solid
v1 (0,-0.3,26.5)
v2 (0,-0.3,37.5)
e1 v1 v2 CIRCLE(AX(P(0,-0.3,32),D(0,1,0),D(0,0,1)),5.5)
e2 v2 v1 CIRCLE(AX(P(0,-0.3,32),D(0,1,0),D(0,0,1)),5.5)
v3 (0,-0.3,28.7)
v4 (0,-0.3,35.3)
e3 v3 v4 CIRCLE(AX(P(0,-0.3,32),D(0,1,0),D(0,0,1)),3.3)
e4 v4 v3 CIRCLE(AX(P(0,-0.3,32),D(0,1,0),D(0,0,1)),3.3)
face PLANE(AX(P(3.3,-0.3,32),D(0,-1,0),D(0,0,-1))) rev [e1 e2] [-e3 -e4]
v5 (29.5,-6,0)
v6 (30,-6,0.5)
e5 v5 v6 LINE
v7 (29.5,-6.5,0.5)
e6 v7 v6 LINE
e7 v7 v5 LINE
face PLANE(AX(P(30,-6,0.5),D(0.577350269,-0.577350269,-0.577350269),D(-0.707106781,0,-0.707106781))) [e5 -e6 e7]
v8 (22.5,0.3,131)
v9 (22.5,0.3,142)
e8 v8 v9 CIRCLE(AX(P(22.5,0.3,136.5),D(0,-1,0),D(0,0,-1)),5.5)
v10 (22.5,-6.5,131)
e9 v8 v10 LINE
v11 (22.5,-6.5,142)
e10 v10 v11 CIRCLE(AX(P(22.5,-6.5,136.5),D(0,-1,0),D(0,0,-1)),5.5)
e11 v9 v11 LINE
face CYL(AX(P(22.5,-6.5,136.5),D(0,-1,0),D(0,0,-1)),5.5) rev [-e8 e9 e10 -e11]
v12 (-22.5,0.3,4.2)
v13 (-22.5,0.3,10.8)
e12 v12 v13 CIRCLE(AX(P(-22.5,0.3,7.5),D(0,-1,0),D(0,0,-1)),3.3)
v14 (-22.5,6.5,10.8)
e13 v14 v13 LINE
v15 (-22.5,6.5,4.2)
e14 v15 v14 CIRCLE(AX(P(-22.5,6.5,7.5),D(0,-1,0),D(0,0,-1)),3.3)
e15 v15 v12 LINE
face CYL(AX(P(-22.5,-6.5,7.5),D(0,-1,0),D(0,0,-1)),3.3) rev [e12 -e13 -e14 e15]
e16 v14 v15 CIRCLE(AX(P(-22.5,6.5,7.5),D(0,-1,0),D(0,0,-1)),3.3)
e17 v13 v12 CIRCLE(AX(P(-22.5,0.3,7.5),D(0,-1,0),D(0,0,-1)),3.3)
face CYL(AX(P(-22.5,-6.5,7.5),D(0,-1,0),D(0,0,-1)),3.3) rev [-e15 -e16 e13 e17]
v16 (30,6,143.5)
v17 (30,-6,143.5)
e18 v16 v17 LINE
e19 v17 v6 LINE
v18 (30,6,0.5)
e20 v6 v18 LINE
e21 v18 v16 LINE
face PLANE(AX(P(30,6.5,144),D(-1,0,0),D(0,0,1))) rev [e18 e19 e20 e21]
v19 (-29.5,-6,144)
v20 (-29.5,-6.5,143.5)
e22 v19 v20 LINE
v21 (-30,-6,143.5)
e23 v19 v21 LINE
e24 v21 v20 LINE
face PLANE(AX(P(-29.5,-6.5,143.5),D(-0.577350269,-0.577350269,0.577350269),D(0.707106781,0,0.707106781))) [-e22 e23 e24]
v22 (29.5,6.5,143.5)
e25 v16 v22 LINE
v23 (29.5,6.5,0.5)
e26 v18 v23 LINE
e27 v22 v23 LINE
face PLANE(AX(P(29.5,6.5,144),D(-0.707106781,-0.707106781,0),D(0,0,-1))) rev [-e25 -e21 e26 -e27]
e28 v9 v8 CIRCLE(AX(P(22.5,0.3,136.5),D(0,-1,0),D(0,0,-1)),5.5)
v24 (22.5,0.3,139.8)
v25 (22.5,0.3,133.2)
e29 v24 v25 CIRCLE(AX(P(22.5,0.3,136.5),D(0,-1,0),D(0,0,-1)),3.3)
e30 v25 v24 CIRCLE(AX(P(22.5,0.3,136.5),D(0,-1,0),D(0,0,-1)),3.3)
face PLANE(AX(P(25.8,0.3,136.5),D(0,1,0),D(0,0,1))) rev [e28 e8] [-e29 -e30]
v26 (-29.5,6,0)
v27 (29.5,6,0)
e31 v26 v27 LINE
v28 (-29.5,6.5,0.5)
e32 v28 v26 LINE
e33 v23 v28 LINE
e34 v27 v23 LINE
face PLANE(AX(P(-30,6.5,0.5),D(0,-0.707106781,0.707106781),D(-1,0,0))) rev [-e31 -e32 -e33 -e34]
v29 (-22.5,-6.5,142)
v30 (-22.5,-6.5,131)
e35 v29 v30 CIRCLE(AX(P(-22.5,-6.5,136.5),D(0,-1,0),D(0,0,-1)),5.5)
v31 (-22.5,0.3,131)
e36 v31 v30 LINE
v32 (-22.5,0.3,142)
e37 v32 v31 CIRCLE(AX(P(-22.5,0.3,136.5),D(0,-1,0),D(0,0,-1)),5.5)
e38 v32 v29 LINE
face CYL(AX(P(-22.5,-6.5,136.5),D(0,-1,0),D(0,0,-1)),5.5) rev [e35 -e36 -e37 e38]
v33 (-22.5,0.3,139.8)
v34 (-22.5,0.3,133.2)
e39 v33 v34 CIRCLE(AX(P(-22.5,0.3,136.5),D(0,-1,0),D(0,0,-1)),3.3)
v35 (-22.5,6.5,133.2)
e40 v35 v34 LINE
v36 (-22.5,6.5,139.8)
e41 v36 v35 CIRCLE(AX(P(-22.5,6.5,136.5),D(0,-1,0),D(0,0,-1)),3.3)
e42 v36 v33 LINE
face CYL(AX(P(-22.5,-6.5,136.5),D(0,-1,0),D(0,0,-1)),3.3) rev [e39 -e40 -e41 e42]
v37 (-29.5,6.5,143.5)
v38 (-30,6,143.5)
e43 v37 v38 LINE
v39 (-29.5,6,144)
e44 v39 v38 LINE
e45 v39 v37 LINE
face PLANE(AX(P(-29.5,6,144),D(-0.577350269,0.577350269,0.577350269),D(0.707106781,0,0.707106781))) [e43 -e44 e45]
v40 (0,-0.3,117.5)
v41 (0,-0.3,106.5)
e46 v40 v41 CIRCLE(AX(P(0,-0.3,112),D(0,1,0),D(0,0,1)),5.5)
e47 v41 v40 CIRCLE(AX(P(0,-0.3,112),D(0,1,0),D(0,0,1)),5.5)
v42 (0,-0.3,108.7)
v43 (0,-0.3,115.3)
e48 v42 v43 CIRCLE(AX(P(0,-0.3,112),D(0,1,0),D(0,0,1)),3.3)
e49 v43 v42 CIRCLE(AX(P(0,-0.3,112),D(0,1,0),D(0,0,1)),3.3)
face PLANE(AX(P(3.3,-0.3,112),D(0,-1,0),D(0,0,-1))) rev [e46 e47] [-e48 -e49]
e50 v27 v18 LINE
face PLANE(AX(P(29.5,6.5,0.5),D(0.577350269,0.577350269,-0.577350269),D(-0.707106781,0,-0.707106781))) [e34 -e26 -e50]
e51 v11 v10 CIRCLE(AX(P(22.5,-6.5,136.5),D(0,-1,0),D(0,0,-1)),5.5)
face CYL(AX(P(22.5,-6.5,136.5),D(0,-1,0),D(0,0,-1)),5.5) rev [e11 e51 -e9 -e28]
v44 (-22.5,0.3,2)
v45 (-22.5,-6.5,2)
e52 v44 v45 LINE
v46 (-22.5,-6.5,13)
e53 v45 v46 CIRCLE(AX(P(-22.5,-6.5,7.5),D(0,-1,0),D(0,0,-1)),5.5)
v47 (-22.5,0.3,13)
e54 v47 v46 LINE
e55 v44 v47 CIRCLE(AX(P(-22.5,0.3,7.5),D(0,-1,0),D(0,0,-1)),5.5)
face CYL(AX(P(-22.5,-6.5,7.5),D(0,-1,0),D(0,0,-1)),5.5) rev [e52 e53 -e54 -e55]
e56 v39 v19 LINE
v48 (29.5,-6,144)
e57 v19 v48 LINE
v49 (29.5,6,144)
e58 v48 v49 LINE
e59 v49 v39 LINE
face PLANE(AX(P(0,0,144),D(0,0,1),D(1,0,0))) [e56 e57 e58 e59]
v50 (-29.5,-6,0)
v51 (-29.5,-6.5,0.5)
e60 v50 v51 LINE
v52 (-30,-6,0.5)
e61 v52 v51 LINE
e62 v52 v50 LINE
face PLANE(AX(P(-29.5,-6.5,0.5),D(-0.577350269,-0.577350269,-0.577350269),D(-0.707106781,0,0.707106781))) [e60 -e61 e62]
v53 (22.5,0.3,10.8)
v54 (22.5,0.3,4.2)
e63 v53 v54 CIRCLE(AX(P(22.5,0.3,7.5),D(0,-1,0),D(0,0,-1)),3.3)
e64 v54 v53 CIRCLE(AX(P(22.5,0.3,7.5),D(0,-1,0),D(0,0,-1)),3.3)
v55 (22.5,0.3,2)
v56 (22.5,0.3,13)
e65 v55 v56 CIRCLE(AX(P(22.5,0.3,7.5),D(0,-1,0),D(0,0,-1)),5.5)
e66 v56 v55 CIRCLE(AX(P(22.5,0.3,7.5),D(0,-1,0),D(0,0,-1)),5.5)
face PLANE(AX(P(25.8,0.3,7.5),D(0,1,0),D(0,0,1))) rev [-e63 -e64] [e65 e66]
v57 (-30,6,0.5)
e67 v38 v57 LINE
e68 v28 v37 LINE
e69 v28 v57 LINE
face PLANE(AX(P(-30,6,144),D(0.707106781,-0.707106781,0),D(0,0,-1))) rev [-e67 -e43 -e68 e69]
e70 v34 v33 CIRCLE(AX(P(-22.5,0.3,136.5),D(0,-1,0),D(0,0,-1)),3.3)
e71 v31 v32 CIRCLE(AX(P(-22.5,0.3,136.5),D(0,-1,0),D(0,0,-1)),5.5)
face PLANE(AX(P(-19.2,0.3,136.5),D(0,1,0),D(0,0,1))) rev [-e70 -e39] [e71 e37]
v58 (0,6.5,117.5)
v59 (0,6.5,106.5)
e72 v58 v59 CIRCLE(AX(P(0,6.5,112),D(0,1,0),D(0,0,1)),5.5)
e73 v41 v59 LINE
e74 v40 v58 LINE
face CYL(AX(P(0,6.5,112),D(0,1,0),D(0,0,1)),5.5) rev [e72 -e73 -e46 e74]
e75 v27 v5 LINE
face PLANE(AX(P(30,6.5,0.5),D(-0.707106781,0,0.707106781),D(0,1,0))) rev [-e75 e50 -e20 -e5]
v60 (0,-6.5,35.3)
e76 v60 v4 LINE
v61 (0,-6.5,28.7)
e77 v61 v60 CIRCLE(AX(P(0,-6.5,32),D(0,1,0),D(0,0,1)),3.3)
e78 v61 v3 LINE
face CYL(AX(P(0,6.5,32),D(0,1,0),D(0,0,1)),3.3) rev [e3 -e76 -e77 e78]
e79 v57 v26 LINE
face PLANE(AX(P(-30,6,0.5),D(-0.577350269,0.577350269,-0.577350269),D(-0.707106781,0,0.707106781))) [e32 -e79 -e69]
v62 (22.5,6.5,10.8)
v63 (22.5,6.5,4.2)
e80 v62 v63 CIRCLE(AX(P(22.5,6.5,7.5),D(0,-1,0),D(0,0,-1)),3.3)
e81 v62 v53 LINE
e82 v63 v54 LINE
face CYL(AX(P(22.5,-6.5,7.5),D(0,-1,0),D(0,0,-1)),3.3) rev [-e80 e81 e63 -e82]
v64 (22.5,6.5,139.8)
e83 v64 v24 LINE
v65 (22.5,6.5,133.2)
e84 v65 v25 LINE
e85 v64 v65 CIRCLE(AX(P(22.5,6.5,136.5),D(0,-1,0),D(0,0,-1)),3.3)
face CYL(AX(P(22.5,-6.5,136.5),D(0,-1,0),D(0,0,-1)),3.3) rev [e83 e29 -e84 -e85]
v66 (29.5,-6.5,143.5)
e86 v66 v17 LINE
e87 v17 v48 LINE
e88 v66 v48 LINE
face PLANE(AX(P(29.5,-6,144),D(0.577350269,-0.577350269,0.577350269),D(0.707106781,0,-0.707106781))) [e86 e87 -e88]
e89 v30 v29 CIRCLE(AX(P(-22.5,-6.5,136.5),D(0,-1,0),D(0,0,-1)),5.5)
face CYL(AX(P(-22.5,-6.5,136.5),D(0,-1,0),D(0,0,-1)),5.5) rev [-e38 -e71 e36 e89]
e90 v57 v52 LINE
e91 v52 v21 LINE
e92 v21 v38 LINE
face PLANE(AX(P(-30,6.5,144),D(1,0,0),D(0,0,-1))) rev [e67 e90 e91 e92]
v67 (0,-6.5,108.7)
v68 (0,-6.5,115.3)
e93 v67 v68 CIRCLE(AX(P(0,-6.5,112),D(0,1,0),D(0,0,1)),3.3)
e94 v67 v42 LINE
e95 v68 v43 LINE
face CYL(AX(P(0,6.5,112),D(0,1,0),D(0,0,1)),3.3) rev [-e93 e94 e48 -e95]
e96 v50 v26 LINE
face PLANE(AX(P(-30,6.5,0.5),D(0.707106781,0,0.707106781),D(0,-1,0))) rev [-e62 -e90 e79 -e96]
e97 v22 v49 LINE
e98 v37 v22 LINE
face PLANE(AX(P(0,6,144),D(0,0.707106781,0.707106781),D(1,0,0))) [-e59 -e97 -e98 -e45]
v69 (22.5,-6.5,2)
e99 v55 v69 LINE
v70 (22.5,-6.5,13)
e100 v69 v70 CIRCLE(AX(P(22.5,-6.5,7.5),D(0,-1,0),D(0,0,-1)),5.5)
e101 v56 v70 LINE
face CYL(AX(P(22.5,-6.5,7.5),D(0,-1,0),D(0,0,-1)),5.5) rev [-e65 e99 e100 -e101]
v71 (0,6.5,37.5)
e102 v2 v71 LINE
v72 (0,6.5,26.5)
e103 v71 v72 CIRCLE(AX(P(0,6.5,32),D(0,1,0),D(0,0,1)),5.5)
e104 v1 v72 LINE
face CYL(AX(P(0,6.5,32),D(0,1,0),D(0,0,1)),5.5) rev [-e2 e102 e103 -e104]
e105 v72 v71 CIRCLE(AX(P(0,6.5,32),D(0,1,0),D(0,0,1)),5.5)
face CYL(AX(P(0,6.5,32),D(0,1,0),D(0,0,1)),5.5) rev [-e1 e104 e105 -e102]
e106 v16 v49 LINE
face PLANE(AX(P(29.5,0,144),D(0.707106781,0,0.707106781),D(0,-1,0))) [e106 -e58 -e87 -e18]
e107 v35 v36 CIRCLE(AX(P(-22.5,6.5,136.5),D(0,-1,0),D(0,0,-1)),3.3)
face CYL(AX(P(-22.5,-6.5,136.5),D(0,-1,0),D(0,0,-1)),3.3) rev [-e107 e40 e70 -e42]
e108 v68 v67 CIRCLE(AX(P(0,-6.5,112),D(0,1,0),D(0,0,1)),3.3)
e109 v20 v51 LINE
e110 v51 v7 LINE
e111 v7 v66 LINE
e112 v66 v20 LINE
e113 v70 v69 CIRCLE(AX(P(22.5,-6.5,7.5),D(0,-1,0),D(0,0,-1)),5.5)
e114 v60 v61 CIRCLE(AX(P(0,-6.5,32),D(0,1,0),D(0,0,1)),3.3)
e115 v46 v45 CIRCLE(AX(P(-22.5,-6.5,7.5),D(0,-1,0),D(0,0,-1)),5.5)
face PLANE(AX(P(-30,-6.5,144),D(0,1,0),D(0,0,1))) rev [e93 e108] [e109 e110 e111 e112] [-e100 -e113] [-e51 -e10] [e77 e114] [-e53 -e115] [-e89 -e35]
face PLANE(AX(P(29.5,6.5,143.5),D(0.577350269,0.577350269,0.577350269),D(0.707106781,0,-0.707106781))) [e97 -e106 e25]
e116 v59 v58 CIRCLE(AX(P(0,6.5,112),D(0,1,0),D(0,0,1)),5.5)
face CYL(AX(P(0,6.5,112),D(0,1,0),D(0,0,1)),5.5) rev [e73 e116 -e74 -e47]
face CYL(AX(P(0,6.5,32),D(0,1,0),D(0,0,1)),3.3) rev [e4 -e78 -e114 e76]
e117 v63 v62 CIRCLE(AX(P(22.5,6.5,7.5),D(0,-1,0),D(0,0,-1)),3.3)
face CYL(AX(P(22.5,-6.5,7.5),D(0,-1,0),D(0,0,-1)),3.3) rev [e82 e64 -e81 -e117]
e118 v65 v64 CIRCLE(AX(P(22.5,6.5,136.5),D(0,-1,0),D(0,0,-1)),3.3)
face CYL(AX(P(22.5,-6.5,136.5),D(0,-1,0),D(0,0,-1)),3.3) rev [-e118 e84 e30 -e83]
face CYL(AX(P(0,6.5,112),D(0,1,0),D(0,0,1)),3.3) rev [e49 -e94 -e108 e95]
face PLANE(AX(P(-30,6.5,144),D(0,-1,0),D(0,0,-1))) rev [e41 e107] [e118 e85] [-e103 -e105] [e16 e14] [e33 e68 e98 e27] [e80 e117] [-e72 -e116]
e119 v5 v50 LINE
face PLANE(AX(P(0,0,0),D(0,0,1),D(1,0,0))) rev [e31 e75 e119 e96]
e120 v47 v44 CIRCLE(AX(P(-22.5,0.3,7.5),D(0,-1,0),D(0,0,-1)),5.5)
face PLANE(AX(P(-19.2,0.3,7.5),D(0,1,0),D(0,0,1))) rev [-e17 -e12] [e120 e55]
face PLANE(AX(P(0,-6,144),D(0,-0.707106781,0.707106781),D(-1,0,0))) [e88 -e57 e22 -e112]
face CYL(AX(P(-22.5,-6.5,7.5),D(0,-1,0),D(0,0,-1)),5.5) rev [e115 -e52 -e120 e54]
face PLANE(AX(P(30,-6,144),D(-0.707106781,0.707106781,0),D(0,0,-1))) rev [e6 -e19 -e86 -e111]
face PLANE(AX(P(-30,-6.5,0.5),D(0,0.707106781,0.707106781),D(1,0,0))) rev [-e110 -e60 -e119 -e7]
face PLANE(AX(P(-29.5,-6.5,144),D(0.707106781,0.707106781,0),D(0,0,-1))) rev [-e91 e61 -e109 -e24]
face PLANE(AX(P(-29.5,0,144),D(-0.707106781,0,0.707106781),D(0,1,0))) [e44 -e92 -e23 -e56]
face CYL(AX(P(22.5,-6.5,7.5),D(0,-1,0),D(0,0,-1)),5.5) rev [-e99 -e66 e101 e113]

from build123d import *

# Parameters (mm, degrees)
SKETCH_1_W                  = 60
SKETCH_1_H                  = 13
EXTRUDE_1_DEPTH             = 144
HOLE_WIZARD_2_D             = 6.6
HOLE_WIZARD_2_CBORE_D       = 11
HOLE_WIZARD_2_CBORE_DEPTH   = 6.8
CHAMFER_1_SIZE              = 0.5
HOLE_WIZARD_2_2_D           = 6.6
HOLE_WIZARD_2_2_CBORE_D     = 11
HOLE_WIZARD_2_2_CBORE_DEPTH = 6.8


with BuildPart() as part:
    # 草图1 → 凸台-拉伸1 (new body)
    with BuildSketch(Plane.XY):
        Rectangle(SKETCH_1_W, SKETCH_1_H)
    extrude(amount=EXTRUDE_1_DEPTH)

    # Hole Wizard 2 (through all)
    with Locations(Plane(origin=(0, 6.5, 0), x_dir=(1, 0, 0), z_dir=(0, 1, 0))):
        with Locations((0, -32), (0, -112)):
            CounterBoreHole(HOLE_WIZARD_2_D / 2, HOLE_WIZARD_2_CBORE_D / 2, HOLE_WIZARD_2_CBORE_DEPTH)

    # 倒角1
    chamfer_1_edges = [part.edges().sort_by_distance(p)[0] for p in [
        (-30, 0, 144),
        (0, -6.5, 144),
        (30, 0, 144),
        (0, -6.5, 0),
        (-30, 0, 0),
        (0, 6.5, 0),
        (30, 0, 0),
        (0, 6.5, 144),
        (30, -6.5, 72),
        (-30, -6.5, 72),
        (-30, 6.5, 72),
        (30, 6.5, 72),
    ]]
    chamfer(chamfer_1_edges, length=CHAMFER_1_SIZE)

    # Hole Wizard 2 2 (through all)
    with Locations(Plane(origin=(0, -6.5, 0), x_dir=(-1, 0, 0), z_dir=(0, -1, 0))):
        with Locations((-22.5, -136.5), (22.5, -136.5), (-22.5, -7.5), (22.5, -7.5)):
            CounterBoreHole(HOLE_WIZARD_2_2_D / 2, HOLE_WIZARD_2_2_CBORE_D / 2, HOLE_WIZARD_2_2_CBORE_DEPTH)


solid = part.part
